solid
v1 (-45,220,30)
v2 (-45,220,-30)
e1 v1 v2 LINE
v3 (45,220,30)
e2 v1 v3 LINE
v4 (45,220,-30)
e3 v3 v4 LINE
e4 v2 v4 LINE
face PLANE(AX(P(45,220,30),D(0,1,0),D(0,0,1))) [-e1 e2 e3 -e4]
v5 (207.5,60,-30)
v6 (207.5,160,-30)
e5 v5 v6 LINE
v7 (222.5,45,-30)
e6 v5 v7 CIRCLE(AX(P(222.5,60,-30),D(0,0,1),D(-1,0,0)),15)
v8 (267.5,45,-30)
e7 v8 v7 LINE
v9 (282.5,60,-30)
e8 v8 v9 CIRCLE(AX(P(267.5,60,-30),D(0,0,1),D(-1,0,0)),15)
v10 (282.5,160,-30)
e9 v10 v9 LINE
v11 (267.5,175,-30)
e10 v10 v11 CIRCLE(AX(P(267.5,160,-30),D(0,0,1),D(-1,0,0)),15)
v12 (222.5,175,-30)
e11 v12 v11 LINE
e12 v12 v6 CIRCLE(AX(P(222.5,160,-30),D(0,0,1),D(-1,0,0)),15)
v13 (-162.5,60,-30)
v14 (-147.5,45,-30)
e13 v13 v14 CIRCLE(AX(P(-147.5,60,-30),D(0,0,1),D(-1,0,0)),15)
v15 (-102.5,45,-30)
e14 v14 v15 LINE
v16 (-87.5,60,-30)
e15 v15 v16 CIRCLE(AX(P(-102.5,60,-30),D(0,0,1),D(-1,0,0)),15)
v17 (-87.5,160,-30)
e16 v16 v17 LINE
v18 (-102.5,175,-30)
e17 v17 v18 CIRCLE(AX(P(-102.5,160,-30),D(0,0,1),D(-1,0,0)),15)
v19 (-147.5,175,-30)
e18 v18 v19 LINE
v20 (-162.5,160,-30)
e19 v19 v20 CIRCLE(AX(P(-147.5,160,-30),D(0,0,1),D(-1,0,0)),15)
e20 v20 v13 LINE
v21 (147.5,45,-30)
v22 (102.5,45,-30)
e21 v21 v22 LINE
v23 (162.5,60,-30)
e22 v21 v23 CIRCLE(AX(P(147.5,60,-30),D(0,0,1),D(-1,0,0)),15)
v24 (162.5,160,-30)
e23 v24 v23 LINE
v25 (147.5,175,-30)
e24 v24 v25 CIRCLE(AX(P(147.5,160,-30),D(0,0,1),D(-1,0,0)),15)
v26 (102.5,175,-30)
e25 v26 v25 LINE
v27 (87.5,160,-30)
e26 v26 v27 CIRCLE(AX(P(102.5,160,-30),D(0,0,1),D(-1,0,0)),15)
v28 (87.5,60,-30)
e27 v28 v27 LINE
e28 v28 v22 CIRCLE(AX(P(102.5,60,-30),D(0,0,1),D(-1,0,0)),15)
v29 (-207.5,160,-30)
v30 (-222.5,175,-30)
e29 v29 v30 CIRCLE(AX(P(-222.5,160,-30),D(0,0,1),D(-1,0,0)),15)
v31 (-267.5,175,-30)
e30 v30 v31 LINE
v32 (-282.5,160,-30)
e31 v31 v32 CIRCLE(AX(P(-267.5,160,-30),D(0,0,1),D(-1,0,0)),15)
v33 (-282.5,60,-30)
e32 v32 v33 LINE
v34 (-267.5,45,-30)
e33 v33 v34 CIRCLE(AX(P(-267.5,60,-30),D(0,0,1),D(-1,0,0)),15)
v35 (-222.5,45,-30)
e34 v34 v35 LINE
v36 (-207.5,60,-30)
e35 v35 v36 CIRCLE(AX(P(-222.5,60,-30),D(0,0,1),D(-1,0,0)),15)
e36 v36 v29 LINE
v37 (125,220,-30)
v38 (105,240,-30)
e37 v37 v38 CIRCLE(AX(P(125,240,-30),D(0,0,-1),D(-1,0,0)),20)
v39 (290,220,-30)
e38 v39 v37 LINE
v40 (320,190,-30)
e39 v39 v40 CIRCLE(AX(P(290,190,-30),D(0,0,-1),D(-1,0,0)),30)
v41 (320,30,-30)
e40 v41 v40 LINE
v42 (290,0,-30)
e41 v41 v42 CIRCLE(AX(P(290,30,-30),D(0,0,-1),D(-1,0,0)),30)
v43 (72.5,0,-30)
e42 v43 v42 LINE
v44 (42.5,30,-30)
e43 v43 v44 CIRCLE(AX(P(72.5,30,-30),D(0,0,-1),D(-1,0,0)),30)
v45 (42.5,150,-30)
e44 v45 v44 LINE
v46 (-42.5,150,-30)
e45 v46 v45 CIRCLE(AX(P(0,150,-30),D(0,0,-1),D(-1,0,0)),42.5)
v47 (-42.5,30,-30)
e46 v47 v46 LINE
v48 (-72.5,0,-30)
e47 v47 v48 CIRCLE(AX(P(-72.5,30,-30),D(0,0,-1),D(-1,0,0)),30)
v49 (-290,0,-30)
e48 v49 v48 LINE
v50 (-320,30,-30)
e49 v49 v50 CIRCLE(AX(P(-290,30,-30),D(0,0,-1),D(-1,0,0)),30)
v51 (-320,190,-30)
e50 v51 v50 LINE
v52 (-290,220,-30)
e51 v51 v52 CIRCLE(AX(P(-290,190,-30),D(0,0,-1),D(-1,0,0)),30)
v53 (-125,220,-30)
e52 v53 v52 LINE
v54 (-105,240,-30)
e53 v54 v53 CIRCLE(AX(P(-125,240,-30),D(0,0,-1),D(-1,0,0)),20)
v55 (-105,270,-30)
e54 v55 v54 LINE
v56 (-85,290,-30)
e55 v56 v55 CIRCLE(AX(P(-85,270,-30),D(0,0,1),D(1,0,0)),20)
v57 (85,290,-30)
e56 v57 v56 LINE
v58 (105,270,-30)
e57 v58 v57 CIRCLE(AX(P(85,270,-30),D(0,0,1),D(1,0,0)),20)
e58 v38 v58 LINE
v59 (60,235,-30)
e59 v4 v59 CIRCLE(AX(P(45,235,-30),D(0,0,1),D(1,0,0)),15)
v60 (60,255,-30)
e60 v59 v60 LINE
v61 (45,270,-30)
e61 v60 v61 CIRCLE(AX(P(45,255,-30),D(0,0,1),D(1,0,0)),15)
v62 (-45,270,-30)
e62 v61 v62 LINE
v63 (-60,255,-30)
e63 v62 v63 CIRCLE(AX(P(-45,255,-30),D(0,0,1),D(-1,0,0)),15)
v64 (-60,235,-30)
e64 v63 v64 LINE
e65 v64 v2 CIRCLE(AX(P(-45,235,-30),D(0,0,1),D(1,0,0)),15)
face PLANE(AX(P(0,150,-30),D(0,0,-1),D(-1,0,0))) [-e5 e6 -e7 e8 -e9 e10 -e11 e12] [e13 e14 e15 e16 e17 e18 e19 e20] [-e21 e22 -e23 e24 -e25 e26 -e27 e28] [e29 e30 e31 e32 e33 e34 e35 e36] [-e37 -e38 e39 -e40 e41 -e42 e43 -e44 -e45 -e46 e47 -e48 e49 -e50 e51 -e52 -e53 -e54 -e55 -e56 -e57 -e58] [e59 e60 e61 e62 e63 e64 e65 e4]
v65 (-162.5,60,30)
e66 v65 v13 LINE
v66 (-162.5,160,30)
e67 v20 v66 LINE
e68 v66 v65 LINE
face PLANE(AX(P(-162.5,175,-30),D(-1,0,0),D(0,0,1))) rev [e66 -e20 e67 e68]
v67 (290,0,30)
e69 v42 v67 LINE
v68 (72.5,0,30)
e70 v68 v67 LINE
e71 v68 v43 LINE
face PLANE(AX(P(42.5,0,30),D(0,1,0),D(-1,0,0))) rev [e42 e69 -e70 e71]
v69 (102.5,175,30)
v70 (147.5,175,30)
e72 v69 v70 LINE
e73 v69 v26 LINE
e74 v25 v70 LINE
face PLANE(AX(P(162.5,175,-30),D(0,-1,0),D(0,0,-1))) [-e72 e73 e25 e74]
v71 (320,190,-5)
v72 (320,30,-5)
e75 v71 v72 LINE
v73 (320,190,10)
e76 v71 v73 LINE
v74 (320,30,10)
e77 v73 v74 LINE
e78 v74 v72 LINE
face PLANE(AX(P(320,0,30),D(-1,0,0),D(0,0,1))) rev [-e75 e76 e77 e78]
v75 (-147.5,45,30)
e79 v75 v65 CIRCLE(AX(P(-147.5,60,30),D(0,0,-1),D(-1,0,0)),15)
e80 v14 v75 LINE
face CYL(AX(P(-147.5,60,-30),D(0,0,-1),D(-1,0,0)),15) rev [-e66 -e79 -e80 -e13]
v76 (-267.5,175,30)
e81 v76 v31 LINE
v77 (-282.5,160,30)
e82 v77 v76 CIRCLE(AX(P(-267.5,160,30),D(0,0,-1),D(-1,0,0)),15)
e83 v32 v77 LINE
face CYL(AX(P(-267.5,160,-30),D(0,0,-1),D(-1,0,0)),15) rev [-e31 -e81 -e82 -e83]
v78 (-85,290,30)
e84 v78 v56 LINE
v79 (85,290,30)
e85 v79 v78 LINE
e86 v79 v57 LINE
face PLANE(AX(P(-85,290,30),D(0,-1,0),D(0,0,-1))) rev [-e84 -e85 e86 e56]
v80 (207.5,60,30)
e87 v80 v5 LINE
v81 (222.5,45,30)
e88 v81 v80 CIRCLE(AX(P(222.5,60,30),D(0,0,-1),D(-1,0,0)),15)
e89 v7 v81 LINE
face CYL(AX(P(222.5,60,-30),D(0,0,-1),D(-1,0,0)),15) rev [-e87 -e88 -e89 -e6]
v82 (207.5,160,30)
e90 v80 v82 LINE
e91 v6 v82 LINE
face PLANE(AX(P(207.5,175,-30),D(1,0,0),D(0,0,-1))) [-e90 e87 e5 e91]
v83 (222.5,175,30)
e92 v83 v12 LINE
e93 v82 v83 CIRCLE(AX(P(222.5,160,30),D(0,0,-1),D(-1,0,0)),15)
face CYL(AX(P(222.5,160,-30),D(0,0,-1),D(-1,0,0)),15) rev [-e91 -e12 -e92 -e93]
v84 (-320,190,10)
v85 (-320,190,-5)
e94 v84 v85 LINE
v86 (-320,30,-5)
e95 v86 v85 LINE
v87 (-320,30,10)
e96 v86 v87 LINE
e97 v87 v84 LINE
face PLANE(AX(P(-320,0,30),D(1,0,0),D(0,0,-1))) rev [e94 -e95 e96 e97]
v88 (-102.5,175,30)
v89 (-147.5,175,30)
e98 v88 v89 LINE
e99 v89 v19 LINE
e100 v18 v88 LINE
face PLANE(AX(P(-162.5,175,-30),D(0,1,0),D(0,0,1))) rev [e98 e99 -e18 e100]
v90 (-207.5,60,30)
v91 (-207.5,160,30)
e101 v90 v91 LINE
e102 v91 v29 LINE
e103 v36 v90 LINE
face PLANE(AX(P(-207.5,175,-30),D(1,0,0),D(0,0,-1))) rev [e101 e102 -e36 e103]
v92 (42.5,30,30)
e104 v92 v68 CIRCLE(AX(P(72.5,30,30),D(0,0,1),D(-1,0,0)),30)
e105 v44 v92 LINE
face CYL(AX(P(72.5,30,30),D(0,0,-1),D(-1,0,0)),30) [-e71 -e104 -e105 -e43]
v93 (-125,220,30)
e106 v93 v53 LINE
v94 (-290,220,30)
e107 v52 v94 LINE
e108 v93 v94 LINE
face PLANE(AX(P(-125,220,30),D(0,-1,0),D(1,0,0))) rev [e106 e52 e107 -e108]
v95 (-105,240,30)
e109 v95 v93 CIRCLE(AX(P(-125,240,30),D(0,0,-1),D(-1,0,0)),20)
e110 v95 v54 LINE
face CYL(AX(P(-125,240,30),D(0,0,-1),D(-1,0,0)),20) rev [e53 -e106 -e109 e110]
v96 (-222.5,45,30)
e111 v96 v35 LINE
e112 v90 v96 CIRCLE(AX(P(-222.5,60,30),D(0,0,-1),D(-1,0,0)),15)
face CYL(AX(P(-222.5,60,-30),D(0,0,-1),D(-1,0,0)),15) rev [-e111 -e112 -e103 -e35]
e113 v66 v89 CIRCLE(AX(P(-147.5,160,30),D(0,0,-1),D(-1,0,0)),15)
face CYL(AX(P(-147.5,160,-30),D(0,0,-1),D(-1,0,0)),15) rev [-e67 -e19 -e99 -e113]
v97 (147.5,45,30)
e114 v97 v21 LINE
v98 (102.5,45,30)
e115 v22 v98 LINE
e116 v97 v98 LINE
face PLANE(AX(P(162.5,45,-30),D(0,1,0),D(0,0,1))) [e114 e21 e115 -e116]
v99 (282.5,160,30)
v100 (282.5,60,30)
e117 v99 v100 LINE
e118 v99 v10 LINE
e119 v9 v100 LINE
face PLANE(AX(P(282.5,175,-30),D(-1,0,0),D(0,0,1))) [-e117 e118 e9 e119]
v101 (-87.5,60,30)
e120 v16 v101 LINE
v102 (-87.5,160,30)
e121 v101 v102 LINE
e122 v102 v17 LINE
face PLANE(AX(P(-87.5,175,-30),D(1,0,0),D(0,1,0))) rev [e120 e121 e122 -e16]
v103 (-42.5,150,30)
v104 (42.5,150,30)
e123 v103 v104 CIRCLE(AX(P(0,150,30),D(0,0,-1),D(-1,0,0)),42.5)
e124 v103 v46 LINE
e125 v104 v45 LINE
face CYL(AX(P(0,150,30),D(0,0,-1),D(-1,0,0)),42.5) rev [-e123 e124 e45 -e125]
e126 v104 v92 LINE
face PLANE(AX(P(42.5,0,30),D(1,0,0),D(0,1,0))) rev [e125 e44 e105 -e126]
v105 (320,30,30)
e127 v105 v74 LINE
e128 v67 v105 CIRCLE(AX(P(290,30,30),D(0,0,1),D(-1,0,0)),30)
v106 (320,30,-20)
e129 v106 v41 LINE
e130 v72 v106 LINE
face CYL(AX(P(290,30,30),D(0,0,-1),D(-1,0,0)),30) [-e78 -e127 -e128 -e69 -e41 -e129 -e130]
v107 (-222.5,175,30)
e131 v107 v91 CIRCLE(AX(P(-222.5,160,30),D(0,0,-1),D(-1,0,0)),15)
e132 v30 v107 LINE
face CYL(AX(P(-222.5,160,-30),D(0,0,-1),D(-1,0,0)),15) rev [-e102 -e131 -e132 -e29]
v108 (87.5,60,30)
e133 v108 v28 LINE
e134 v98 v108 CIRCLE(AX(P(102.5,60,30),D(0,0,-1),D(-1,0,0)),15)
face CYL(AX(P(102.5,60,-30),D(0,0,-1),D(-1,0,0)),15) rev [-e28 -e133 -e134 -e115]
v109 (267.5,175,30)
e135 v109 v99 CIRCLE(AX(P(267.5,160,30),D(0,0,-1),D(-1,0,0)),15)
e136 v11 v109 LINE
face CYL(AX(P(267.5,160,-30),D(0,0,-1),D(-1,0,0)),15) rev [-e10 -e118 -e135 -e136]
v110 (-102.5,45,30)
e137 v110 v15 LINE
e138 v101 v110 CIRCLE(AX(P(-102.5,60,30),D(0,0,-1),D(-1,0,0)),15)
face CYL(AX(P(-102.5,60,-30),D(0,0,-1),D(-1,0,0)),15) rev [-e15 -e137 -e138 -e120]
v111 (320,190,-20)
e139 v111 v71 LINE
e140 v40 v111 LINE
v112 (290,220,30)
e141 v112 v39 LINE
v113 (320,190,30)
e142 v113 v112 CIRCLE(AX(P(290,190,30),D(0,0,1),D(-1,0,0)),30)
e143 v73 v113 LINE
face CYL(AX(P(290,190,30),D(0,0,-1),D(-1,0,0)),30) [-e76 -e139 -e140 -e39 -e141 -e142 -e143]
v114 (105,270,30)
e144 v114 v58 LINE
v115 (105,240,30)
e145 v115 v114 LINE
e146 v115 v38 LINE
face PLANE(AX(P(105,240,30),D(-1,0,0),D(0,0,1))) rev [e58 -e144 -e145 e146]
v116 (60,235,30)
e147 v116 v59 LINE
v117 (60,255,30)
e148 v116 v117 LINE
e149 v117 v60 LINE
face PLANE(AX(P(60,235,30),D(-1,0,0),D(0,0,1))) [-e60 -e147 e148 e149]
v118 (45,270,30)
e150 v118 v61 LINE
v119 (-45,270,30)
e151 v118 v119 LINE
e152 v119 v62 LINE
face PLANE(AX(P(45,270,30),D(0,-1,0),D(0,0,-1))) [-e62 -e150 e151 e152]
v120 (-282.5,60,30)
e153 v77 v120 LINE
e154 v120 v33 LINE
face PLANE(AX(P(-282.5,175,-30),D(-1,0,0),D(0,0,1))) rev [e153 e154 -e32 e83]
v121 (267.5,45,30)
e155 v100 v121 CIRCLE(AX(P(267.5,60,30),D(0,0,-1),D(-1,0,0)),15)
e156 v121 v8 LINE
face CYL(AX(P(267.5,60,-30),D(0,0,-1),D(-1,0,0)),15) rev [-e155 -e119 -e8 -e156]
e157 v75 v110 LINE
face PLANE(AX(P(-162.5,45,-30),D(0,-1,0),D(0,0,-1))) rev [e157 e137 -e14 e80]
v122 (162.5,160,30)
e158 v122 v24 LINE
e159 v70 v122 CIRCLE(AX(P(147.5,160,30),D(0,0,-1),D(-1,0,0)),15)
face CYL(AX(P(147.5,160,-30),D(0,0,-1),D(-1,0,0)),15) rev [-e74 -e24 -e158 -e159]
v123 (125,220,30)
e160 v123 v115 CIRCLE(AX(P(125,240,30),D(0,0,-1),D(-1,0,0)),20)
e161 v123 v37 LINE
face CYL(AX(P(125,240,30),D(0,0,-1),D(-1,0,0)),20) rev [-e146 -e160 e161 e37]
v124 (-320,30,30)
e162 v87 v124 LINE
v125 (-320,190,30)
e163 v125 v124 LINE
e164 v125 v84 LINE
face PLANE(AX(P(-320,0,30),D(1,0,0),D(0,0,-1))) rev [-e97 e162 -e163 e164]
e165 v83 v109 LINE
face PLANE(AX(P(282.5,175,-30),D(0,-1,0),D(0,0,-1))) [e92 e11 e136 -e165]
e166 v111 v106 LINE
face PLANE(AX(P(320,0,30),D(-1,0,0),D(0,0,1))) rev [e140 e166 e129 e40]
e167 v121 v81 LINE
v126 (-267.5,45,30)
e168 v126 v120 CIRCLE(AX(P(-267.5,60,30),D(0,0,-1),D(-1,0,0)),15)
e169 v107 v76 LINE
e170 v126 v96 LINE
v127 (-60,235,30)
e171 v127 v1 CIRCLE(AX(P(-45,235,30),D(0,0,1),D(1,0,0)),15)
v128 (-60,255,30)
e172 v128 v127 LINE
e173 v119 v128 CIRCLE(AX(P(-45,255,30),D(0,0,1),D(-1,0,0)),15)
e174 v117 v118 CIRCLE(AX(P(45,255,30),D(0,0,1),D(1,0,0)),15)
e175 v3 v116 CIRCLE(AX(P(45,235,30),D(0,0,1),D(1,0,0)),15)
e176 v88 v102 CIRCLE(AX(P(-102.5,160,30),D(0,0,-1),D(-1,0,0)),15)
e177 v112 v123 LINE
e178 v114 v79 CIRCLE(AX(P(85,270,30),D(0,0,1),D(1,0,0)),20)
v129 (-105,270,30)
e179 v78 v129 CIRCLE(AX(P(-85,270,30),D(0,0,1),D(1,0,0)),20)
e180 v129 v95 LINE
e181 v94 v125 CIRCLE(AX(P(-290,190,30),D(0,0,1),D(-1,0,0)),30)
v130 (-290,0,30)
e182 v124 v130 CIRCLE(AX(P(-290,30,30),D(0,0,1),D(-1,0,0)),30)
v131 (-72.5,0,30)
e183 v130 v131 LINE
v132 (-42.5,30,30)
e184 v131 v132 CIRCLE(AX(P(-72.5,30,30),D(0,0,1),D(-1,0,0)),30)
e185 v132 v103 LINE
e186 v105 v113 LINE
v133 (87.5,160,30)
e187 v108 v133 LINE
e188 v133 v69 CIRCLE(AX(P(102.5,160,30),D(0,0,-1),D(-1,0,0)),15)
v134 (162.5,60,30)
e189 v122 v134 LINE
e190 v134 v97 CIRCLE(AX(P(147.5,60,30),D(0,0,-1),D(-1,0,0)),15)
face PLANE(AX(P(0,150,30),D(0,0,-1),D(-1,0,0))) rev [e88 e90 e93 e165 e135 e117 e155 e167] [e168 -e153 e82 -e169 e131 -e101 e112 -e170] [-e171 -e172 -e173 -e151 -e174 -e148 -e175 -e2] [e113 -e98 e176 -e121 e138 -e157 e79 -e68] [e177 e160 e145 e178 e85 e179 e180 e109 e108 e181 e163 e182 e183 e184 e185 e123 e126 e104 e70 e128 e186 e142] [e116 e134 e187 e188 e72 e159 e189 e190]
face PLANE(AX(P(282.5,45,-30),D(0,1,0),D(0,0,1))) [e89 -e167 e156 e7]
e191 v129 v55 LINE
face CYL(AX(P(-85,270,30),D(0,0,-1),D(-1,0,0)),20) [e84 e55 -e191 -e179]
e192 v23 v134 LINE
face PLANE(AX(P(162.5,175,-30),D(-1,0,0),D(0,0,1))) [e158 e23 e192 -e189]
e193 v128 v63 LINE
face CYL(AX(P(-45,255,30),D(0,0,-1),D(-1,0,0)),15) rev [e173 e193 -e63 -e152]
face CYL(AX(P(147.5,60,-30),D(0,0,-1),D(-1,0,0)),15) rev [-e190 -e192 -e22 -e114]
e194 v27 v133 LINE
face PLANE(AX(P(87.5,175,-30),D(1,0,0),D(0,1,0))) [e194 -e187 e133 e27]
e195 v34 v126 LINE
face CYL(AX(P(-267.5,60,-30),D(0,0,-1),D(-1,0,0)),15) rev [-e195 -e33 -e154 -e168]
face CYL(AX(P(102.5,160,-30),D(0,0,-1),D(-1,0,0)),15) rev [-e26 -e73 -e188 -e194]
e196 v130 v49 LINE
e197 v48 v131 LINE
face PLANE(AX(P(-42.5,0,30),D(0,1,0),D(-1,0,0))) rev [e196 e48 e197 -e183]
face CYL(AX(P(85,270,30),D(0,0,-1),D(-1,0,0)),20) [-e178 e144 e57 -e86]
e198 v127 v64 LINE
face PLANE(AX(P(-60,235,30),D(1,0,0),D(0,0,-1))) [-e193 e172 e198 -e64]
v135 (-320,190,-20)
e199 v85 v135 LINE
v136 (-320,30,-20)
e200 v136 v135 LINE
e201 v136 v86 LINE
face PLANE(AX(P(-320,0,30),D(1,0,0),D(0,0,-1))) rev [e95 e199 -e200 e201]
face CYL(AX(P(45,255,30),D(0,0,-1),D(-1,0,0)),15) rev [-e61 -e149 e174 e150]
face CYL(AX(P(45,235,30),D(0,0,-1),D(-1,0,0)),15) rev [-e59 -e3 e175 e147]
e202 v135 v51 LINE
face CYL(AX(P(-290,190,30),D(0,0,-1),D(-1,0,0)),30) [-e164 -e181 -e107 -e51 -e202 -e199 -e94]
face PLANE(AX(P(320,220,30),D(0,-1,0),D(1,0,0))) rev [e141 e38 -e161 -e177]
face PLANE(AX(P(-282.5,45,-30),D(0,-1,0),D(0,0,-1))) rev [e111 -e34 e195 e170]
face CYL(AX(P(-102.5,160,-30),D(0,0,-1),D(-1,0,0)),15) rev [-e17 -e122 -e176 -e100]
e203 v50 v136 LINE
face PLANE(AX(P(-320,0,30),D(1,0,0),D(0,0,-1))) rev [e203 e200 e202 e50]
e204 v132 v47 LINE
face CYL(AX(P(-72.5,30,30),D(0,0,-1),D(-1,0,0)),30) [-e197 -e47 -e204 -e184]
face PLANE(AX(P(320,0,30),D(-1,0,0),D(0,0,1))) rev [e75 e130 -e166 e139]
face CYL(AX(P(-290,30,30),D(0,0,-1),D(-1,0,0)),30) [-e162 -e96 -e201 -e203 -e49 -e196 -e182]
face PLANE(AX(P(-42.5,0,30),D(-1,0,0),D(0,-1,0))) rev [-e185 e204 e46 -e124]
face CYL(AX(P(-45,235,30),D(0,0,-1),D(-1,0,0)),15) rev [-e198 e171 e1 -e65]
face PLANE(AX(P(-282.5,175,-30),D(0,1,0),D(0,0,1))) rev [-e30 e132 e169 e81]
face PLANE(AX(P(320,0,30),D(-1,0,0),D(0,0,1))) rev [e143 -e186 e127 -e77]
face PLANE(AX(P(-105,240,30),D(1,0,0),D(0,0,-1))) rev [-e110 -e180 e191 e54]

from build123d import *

# Parameters (mm, degrees)
BOSS_EXTRUDE1_DEPTH  = 30
SKETCH5_W            = 75
SKETCH5_H            = 130
CUT_EXTRUDE3_DEPTH   = 433.897216438
FILLET2_R            = 15
FILLET2_OF_MIRROR3_R = 15
FILLET3_R            = 30


with BuildPart() as part:
    # Sketch1 → Boss-Extrude1 (new, symmetric)
    with BuildSketch(Plane.XY):
        with BuildLine():
            Line((42.5, 0), (320, 0))
            Line((320, 0), (320, 220))
            Line((320, 220), (125, 220))
            ThreePointArc((125, 220), (110.857864376, 225.857864376), (105, 240))
            Line((105, 240), (105, 270))
            ThreePointArc((105, 270), (99.142135624, 284.142135624), (85, 290))
            Line((85, 290), (-85, 290))
            ThreePointArc((-85, 290), (-99.142135624, 284.142135624), (-105, 270))
            Line((-105, 270), (-105, 240))
            ThreePointArc((-105, 240), (-110.857864376, 225.857864376), (-125, 220))
            Line((-125, 220), (-320, 220))
            Line((-320, 220), (-320, 0))
            Line((-320, 0), (-42.5, 0))
            Line((-42.5, 0), (-42.5, 150))
            ThreePointArc((-42.5, 150), (0, 192.5), (42.5, 150))
            Line((42.5, 150), (42.5, 0))
        make_face()
        with BuildLine():
            Line((45, 220), (-45, 220))
            ThreePointArc((-45, 220), (-55.606601718, 224.393398282), (-60, 235))
            Line((-60, 235), (-60, 255))
            ThreePointArc((-60, 255), (-55.606601718, 265.606601718), (-45, 270))
            Line((-45, 270), (45, 270))
            ThreePointArc((45, 270), (55.606601718, 265.606601718), (60, 255))
            Line((60, 255), (60, 235))
            ThreePointArc((60, 235), (55.606601718, 224.393398282), (45, 220))
        make_face(mode=Mode.SUBTRACT)
    extrude(amount=BOSS_EXTRUDE1_DEPTH, both=True)

    # Sketch5 → Cut-Extrude3 (cut, symmetric)
    with BuildSketch(Plane.XY):
        with Locations((-245, 110)):
            Rectangle(SKETCH5_W, SKETCH5_H)
        with Locations((-125, 110)):
            Rectangle(SKETCH5_W, SKETCH5_H)
    cut_extrude3 = extrude(amount=CUT_EXTRUDE3_DEPTH, both=True, mode=Mode.SUBTRACT)

    # Fillet2
    fillet2_edges = [part.edges().sort_by_distance(p)[0] for p in [
        (-207.5, 175, 0),
        (-207.5, 45, 0),
        (-282.5, 45, 0),
        (-282.5, 175, 0),
        (-87.5, 175, 0),
        (-87.5, 45, 0),
        (-162.5, 45, 0),
        (-162.5, 175, 0),
    ]]
    fillet(fillet2_edges, radius=FILLET2_R)

    # Mirror3: Cut-Extrude3 across plane
    add(cut_extrude3.mirror(Plane(origin=(0, 0, 0), x_dir=(0, 0, 1), z_dir=(1, 0, 0))), mode=Mode.SUBTRACT)

    # Fillet2 of Mirror3
    fillet2_of_mirror3_edges = [part.edges().sort_by_distance(p)[0] for p in [
        (207.5, 175, 0),
        (207.5, 45, 0),
        (282.5, 45, 0),
        (282.5, 175, 0),
        (87.5, 175, 0),
        (87.5, 45, 0),
        (162.5, 45, 0),
        (162.5, 175, 0),
    ]]
    fillet(fillet2_of_mirror3_edges, radius=FILLET2_OF_MIRROR3_R)

    # Fillet3
    fillet3_edges = [part.edges().sort_by_distance(p)[0] for p in [
        (-42.5, 0, 0),
        (-320, 0, 0),
        (-320, 220, 0),
        (320, 220, 0),
        (320, 0, 0),
        (42.5, 0, 0),
    ]]
    fillet(fillet3_edges, radius=FILLET3_R)


solid = part.part
